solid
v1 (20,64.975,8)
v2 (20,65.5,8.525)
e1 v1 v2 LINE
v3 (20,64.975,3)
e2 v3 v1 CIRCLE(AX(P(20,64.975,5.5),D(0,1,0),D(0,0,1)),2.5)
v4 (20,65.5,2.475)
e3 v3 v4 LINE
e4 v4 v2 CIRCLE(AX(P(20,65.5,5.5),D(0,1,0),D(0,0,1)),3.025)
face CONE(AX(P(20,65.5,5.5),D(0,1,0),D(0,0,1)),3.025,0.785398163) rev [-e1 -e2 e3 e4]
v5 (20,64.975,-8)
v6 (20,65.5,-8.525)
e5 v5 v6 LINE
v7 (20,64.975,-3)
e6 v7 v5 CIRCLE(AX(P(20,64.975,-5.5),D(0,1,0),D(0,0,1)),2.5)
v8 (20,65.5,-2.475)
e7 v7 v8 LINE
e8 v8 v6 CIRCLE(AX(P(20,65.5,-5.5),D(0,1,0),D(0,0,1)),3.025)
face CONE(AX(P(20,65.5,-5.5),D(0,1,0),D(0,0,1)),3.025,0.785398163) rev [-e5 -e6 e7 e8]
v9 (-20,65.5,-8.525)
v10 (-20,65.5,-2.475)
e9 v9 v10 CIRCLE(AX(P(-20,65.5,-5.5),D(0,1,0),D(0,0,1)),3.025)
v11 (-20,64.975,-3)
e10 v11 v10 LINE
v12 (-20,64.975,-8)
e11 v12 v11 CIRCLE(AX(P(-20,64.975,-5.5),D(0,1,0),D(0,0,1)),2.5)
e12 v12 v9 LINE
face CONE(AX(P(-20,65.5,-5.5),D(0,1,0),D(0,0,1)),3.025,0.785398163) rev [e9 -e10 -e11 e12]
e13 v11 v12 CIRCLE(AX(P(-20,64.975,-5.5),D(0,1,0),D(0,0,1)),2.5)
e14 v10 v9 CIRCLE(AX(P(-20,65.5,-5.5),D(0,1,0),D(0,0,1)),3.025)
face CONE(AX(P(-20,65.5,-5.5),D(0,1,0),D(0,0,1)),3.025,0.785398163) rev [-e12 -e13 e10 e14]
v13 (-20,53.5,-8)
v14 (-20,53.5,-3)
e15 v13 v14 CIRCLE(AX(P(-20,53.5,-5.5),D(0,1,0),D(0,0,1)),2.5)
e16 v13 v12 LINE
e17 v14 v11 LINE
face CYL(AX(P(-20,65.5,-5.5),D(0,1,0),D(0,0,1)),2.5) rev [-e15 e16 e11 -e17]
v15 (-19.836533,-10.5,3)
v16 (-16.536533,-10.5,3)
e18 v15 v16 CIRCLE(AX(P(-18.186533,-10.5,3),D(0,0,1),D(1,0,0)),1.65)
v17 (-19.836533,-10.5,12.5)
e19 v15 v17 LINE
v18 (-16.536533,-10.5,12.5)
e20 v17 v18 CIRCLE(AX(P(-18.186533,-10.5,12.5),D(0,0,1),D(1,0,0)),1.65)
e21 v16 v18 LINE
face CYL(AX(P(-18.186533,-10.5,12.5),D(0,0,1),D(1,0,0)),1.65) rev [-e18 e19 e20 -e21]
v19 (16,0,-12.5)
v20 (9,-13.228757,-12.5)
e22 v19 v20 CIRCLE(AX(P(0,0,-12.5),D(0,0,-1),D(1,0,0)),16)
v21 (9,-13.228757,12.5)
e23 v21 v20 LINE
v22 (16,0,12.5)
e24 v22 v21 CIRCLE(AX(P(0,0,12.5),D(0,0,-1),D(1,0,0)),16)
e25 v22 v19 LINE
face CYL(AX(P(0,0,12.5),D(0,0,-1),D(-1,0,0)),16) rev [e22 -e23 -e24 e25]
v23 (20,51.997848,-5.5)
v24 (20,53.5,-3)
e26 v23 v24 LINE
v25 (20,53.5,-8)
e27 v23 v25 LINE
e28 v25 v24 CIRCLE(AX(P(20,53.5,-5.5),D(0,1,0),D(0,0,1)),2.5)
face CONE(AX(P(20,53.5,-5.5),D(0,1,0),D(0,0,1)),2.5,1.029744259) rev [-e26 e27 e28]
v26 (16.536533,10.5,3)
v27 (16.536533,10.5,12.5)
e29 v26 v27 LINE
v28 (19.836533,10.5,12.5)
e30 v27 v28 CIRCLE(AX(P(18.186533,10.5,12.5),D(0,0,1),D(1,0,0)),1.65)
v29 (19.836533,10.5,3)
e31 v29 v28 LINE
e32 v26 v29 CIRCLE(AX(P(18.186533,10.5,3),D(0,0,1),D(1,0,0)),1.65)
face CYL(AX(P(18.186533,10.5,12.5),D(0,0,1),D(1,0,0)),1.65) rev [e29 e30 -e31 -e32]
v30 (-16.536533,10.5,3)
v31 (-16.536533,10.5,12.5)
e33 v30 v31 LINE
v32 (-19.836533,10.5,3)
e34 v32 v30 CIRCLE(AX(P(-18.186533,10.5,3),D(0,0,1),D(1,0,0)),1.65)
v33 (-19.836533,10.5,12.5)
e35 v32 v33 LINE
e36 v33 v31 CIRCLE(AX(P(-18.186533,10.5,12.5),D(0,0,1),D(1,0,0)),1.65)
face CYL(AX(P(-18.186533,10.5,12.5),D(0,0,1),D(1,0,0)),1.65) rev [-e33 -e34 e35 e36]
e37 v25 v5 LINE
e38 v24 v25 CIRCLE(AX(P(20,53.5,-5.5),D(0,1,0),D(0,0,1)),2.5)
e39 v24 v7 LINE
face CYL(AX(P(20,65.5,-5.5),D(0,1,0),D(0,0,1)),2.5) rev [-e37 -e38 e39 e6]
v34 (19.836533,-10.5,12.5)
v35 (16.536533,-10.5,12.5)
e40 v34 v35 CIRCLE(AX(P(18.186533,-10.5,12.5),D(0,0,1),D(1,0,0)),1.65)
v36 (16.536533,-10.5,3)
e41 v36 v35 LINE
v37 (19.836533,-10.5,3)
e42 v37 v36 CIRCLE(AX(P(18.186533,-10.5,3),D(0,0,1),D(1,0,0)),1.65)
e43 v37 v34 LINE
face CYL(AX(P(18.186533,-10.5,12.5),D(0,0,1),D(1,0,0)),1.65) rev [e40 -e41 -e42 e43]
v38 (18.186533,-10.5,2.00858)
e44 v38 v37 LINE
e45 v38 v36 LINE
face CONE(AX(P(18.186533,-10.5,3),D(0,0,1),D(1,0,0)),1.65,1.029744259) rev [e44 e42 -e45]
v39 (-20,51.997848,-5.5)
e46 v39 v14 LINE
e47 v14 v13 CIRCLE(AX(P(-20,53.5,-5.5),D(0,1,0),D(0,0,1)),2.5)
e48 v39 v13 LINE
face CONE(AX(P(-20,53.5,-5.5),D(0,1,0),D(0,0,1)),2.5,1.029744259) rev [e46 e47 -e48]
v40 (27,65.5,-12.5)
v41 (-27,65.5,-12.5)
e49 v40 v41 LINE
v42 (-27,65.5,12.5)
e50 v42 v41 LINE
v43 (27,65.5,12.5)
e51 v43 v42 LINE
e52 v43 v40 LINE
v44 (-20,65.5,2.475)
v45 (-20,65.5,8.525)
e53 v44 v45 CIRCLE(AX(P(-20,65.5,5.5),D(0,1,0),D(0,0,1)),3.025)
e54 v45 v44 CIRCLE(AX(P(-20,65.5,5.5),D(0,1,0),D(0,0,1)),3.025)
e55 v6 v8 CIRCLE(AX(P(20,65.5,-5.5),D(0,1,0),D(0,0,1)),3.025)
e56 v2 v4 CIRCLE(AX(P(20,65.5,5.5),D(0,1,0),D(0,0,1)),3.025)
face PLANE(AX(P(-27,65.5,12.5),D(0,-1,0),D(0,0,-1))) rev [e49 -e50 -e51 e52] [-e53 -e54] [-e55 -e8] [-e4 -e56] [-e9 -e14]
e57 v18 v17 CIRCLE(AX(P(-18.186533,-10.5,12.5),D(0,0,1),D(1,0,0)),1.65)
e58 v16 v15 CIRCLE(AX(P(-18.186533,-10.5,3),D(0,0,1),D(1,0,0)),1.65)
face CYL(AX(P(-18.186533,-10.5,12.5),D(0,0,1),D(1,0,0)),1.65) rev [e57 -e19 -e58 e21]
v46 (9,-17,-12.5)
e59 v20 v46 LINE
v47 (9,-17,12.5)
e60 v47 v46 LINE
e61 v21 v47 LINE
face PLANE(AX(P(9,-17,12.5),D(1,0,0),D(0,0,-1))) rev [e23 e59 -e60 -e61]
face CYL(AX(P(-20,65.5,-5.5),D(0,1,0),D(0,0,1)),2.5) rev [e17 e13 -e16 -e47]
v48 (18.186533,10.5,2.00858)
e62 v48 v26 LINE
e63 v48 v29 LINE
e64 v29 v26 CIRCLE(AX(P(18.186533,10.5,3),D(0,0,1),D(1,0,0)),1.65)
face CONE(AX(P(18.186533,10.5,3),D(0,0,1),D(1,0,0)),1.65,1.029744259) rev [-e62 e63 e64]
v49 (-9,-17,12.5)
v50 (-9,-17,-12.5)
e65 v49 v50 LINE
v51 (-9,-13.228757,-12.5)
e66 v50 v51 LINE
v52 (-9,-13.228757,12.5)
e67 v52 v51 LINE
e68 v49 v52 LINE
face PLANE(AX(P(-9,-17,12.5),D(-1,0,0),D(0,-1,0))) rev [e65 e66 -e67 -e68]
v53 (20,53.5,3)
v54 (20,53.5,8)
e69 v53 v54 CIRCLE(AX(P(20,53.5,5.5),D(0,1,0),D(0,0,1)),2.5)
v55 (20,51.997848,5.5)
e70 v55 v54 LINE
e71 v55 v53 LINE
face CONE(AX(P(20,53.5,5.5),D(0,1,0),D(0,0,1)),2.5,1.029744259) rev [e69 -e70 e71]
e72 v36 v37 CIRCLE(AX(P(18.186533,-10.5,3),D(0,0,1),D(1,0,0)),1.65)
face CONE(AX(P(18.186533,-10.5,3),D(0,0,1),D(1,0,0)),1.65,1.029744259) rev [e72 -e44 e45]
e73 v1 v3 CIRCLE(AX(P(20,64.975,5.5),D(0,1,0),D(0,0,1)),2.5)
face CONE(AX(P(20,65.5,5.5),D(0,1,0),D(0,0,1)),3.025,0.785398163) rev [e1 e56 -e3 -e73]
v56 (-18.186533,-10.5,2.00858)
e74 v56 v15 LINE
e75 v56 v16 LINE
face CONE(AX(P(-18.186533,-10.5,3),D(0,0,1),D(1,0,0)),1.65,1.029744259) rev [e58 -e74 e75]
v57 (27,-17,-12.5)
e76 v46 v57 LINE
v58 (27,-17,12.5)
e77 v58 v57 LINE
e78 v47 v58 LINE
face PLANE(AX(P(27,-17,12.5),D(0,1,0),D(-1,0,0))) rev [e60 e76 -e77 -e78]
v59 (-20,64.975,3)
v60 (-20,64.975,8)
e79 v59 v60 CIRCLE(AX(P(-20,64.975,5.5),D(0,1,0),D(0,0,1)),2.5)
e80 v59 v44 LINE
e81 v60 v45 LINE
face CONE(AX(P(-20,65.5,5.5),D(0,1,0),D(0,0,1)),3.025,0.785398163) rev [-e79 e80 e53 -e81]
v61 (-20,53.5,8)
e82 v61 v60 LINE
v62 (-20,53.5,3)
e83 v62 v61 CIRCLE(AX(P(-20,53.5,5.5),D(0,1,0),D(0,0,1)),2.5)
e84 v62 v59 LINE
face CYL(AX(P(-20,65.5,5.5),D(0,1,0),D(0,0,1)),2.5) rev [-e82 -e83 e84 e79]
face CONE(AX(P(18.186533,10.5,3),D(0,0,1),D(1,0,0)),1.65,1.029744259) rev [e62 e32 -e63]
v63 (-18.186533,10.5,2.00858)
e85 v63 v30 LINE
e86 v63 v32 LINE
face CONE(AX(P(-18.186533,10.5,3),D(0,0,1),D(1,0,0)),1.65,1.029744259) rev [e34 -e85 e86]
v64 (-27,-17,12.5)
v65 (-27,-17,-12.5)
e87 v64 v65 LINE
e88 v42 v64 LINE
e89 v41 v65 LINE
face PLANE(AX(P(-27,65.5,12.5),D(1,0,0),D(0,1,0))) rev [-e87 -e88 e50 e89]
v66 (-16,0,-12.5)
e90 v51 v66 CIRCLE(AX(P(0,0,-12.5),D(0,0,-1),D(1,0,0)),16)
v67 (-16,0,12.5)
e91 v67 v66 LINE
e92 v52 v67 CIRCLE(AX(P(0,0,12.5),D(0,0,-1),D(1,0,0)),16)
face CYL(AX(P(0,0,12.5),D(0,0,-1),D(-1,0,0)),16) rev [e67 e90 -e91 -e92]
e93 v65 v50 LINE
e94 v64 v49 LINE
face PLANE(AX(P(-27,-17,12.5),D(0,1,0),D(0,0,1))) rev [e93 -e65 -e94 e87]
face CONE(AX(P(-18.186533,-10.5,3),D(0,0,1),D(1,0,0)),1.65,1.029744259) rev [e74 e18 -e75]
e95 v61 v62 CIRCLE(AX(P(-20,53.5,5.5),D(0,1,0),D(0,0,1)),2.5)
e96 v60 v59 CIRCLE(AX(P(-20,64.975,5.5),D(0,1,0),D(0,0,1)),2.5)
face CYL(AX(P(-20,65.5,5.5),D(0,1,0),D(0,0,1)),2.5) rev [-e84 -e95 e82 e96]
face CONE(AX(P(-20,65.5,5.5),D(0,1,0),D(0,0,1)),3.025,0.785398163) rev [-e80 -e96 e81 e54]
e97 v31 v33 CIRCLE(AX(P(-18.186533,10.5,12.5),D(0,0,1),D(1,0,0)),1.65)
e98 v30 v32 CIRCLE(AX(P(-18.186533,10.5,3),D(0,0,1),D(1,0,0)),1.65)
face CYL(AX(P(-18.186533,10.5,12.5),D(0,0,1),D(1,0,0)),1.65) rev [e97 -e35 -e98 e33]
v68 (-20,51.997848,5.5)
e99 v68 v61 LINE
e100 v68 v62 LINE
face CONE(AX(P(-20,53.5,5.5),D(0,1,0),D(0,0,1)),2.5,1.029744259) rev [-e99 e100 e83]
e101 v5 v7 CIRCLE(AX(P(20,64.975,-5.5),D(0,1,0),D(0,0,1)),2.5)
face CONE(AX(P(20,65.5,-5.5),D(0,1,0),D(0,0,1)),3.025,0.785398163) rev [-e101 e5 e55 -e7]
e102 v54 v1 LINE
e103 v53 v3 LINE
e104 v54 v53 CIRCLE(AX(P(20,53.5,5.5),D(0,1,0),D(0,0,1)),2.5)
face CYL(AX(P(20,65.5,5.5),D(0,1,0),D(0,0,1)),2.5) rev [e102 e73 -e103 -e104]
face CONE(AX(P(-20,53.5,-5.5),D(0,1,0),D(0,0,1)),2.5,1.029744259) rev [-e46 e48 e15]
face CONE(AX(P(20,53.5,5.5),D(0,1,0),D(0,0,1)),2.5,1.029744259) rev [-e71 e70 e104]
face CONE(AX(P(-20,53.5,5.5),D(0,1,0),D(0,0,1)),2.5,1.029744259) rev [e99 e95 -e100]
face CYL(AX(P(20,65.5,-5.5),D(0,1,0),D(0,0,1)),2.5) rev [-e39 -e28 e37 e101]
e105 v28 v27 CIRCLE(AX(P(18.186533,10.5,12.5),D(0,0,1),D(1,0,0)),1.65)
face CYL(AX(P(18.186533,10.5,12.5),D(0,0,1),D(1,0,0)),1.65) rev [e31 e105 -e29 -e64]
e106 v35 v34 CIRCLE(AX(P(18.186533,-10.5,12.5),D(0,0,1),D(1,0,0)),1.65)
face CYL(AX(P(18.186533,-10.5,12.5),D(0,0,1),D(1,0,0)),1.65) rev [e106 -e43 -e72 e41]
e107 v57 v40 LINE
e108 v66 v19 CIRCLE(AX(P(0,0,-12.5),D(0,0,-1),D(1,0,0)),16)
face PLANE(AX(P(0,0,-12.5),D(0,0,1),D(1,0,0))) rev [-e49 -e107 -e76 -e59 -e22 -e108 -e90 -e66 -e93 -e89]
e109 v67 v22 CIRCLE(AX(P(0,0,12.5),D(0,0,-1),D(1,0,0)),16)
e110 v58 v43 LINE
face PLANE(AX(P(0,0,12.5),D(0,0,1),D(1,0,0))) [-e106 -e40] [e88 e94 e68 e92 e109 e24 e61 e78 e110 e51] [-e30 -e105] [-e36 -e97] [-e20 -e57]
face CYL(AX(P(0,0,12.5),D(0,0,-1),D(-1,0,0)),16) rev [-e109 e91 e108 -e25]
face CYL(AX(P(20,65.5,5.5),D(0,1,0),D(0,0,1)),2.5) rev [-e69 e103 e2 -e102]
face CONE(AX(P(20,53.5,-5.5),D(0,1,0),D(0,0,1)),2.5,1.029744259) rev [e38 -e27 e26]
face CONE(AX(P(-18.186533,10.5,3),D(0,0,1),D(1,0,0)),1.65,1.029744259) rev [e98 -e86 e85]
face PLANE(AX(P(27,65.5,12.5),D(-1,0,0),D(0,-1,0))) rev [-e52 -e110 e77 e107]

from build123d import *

# Parameters (mm, degrees)
EXTRUDE_1_DEPTH              = 12.5
HOLE_WIZARD_M4_1_D           = 3.3
HOLE_WIZARD_M4_1_DEPTH       = 9.5
HOLE_WIZARD_M4_1_TIP         = 0.991420021
HOLE_WIZARD_M6_1_D           = 5
HOLE_WIZARD_M6_1_DEPTH       = 12
HOLE_WIZARD_M6_1_CSINK_D     = 6.05
HOLE_WIZARD_M6_1_CSINK_ANGLE = 90
HOLE_WIZARD_M6_1_TIP         = 1.502151548


with BuildPart() as part:
    # 草图1 → 凸台-拉伸1 (new, symmetric)
    with BuildSketch(Plane.XY):
        with BuildLine():
            Line((-27, 65.5), (27, 65.5))
            Line((27, 65.5), (27, -17))
            Line((27, -17), (9, -17))
            Line((9, -17), (9, -13.228756555))
            ThreePointArc((9, -13.228756555), (0, 16), (-9, -13.228756555))
            Line((-9, -13.228756555), (-9, -17))
            Line((-9, -17), (-27, -17))
            Line((-27, -17), (-27, 65.5))
        make_face()
    extrude(amount=EXTRUDE_1_DEPTH, both=True)

    # M4 螺纹孔1
    with Locations(Plane.XY.offset(12.5)):
        with Locations((18.186533479, 10.5), (18.186533479, -10.5), (-18.186533479, -10.5), (-18.186533479, 10.5)):
            Hole(HOLE_WIZARD_M4_1_D / 2, depth=HOLE_WIZARD_M4_1_DEPTH)
            with Locations((0, 0, -(HOLE_WIZARD_M4_1_DEPTH + HOLE_WIZARD_M4_1_TIP / 2))):  # 118° drill point
                Cone(0, HOLE_WIZARD_M4_1_D / 2, HOLE_WIZARD_M4_1_TIP, mode=Mode.SUBTRACT)

    # M6 螺纹孔1
    with Locations(Plane(origin=(-20, 65.5, 5.5), x_dir=(0, 0, 1), z_dir=(0, 1, 0))):
        with Locations((0, 0), (-11, 0), (-11, 40), (0, 40)):
            CounterSinkHole(HOLE_WIZARD_M6_1_D / 2, HOLE_WIZARD_M6_1_CSINK_D / 2, depth=HOLE_WIZARD_M6_1_DEPTH, counter_sink_angle=HOLE_WIZARD_M6_1_CSINK_ANGLE)
            with Locations((0, 0, -(HOLE_WIZARD_M6_1_DEPTH + HOLE_WIZARD_M6_1_TIP / 2))):  # 118° drill point
                Cone(0, HOLE_WIZARD_M6_1_D / 2, HOLE_WIZARD_M6_1_TIP, mode=Mode.SUBTRACT)


solid = part.part
